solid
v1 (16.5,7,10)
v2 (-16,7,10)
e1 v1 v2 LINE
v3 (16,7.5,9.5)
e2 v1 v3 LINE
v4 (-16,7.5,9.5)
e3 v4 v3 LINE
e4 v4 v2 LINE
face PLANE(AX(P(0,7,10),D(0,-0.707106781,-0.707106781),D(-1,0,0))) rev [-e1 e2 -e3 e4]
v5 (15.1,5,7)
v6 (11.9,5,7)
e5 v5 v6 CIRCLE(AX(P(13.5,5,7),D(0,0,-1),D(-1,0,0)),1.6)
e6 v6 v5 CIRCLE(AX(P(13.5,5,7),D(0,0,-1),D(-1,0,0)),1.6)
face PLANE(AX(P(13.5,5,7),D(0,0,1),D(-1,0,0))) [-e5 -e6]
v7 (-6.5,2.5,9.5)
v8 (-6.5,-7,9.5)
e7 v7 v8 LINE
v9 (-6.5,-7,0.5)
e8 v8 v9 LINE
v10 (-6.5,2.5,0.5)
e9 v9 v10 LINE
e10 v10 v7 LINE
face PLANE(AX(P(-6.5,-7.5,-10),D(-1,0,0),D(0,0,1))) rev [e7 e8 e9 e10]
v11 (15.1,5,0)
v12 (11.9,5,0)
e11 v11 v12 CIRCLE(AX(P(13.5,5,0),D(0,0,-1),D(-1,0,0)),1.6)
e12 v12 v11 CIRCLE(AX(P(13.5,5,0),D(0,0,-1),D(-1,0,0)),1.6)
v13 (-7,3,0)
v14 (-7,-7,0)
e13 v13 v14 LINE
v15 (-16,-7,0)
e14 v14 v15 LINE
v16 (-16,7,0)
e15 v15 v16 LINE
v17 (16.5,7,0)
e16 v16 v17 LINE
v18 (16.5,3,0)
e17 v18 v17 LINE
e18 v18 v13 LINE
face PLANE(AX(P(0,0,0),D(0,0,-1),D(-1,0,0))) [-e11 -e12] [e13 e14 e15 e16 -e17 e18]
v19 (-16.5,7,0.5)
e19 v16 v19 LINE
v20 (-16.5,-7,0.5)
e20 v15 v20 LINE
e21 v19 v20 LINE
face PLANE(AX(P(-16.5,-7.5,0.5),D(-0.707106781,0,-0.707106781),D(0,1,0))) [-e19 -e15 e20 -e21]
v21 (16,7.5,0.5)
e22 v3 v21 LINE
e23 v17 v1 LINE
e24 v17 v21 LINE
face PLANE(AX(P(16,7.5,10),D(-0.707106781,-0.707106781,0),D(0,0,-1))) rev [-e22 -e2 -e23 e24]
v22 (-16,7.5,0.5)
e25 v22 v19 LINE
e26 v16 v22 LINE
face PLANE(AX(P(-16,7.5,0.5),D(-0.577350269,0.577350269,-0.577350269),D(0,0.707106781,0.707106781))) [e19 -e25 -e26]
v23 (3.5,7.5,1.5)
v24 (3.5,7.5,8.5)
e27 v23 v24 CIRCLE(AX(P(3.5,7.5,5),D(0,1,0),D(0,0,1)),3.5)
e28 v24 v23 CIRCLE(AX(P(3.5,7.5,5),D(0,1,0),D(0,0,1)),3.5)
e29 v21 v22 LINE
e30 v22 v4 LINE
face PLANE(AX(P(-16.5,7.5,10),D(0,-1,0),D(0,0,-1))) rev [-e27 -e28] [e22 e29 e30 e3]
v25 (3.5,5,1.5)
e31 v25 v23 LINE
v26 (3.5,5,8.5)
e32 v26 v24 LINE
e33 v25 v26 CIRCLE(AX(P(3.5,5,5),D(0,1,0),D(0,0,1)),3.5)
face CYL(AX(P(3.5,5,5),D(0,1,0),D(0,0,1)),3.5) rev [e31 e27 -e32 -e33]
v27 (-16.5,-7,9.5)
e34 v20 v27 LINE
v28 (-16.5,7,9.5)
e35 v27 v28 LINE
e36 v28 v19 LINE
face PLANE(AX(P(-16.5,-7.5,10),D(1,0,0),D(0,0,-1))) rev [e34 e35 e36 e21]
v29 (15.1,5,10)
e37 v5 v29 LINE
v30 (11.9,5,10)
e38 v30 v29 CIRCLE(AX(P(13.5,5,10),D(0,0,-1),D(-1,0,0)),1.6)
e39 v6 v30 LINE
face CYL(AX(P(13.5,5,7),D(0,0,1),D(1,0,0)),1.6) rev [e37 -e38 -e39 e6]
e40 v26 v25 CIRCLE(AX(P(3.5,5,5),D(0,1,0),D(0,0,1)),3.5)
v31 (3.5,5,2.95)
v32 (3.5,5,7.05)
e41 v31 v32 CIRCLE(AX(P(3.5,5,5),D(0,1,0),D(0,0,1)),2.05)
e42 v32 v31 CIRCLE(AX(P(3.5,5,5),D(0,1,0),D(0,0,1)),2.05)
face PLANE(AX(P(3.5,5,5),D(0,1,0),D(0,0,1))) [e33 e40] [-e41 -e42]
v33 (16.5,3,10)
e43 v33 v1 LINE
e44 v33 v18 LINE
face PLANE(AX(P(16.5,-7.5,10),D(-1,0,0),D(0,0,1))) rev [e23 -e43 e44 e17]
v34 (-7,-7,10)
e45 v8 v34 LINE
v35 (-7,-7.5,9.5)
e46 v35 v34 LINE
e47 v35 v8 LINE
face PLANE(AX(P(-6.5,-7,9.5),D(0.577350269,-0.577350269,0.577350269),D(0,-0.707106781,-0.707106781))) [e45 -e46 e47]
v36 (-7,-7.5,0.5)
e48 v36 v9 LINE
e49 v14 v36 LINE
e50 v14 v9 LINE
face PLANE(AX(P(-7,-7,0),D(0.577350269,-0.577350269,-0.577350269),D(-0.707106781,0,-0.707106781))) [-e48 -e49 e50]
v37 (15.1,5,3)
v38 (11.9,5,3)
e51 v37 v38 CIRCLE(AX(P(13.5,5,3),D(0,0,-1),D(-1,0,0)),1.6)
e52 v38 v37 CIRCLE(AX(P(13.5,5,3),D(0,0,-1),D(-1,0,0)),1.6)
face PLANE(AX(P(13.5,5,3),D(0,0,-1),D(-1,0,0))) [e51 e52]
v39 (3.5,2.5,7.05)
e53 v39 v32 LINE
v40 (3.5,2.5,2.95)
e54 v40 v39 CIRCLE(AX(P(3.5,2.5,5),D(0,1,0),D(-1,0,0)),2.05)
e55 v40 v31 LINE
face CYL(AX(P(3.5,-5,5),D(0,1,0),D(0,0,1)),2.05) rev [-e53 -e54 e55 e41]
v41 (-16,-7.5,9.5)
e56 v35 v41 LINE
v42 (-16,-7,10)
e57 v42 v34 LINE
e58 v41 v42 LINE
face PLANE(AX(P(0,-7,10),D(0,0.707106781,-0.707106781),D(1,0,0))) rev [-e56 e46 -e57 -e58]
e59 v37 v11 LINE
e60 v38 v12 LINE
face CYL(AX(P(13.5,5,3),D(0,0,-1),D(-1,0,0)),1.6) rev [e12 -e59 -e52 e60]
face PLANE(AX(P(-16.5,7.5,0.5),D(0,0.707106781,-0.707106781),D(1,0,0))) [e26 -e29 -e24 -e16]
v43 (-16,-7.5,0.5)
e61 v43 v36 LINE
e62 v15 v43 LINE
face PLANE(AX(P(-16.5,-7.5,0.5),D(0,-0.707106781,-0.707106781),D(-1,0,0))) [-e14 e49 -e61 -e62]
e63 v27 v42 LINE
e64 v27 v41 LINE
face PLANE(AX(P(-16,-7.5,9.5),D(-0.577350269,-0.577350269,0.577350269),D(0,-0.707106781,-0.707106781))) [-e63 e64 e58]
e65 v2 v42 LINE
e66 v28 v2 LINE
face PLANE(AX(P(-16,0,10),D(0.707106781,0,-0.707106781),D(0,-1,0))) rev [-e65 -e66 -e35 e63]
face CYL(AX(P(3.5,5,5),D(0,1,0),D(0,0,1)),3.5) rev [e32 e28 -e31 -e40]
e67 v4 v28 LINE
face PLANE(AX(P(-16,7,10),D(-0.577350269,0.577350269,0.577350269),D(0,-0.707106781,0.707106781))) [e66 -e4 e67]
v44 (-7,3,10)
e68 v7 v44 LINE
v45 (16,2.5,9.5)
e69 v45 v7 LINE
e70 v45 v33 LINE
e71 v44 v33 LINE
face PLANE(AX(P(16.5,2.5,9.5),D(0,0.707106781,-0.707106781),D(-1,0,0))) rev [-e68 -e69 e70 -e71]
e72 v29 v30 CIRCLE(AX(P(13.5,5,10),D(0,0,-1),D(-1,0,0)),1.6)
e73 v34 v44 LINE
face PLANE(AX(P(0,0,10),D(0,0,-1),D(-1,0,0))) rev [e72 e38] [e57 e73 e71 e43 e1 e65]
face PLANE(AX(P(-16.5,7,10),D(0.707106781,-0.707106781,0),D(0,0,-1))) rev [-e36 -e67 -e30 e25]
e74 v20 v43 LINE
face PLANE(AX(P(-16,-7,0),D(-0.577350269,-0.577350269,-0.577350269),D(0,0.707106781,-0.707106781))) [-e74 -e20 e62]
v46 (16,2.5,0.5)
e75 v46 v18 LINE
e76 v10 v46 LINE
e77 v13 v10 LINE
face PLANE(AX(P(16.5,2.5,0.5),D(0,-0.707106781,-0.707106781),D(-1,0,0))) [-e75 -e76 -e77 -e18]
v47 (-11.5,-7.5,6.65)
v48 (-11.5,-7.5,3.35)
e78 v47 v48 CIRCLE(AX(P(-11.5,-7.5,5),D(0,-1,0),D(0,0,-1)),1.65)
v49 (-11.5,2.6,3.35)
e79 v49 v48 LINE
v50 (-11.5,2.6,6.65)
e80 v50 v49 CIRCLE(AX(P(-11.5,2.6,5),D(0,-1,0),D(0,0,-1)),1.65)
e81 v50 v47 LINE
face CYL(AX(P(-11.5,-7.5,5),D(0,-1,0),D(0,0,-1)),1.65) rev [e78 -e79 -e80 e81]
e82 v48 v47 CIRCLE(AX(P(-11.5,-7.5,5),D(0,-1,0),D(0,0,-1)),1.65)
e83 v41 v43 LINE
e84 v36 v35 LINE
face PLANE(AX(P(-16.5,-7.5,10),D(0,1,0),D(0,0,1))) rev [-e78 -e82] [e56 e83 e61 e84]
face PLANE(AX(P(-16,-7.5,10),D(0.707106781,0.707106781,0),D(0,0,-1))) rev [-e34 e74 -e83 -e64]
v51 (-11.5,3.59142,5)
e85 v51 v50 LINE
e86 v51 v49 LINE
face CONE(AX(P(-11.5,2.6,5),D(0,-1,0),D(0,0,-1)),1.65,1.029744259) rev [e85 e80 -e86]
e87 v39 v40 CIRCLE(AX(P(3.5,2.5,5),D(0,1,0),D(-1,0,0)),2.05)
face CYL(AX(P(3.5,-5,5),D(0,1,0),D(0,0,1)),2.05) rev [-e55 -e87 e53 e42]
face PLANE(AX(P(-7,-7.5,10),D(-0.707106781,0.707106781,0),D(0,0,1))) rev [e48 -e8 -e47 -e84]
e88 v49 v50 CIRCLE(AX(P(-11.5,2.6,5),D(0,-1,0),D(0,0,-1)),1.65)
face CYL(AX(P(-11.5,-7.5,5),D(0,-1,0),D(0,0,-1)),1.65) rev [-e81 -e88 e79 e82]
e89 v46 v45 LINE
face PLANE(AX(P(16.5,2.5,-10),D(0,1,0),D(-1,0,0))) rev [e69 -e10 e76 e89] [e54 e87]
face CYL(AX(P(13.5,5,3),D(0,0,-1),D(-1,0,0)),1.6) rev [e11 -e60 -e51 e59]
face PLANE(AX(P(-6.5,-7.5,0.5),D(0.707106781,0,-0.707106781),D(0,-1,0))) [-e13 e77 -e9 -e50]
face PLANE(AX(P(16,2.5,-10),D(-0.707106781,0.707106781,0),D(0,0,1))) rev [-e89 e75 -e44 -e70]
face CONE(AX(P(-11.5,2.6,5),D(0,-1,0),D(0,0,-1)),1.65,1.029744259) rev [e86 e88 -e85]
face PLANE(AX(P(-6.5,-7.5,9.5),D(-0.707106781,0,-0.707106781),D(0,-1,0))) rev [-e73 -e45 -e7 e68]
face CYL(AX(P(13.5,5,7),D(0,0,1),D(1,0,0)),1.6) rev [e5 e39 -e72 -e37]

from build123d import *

# Parameters (mm, degrees)
SKETCH1_W             = 33
SKETCH1_H             = 15
BOSS_EXTRUDE1_DEPTH   = 10
SKETCH2_W             = 23
SKETCH2_H             = 10
CUT_EXTRUDE1_DEPTH    = 20
M4_TAPPED_HOLE1_D     = 3.3
M4_TAPPED_HOLE1_DEPTH = 10.1
M4_TAPPED_HOLE1_TIP   = 0.991420021
CHAMFER1_SIZE         = 0.5
SKETCH6_R             = 3.5
CUT_EXTRUDE3_DEPTH    = 2.5
SKETCH7_R             = 1.6
CUT_EXTRUDE4_DEPTH    = 3
SKETCH8_R             = 2.05
CUT_EXTRUDE5_DEPTH    = 10


with BuildPart() as part:
    # Sketch1 → Boss-Extrude1 (new body)
    with BuildSketch(Plane.XY):
        Rectangle(SKETCH1_W, SKETCH1_H)
    extrude(amount=BOSS_EXTRUDE1_DEPTH)

    # Sketch2 → Cut-Extrude1 (cut)
    with BuildSketch(Plane.XY.offset(10)):
        with Locations((5, -2.5)):
            Rectangle(SKETCH2_W, SKETCH2_H)
    extrude(amount=-CUT_EXTRUDE1_DEPTH, mode=Mode.SUBTRACT)

    # M4 Tapped Hole1
    with Locations(Plane(origin=(0, -7.5, 0), x_dir=(-1, 0, 0), z_dir=(0, -1, 0))):
        with Locations((11.5, -5)):
            Hole(M4_TAPPED_HOLE1_D / 2, depth=M4_TAPPED_HOLE1_DEPTH)
            with Locations((0, 0, -(M4_TAPPED_HOLE1_DEPTH + M4_TAPPED_HOLE1_TIP / 2))):  # 118° drill point
                Cone(0, M4_TAPPED_HOLE1_D / 2, M4_TAPPED_HOLE1_TIP, mode=Mode.SUBTRACT)

    # Chamfer1
    chamfer1_edges = [part.edges().sort_by_distance(p)[0] for p in [
        (-16.5, 0, 10),
        (-11.5, -7.5, 10),
        (5, 2.5, 0),
        (-6.5, -2.5, 0),
        (16.5, 2.5, 5),
        (-6.5, -7.5, 5),
        (5, 2.5, 10),
        (-6.5, -2.5, 10),
        (-11.5, -7.5, 0),
        (-16.5, 0, 0),
        (0, 7.5, 0),
        (0, 7.5, 10),
        (-16.5, -7.5, 5),
        (-16.5, 7.5, 5),
        (16.5, 7.5, 5),
    ]]
    chamfer(chamfer1_edges, length=CHAMFER1_SIZE)

    # Sketch6 → Cut-Extrude3 (cut)
    with BuildSketch(Plane(origin=(0, 7.5, 0), x_dir=(1, 0, 0), z_dir=(0, 1, 0))):
        with Locations(Location((3.5, -5, 0), (0, 0, 270))):
            Circle(SKETCH6_R)
    extrude(amount=-CUT_EXTRUDE3_DEPTH, mode=Mode.SUBTRACT)

    # Sketch7 → Cut-Extrude4 (cut)
    with BuildSketch(Plane(origin=(0, 0, 0), x_dir=(-1, 0, 0), z_dir=(0, 0, -1))):
        with Locations((-13.5, 5)):
            Circle(SKETCH7_R)
    cut_extrude4 = extrude(amount=-CUT_EXTRUDE4_DEPTH, mode=Mode.SUBTRACT)

    # Mirror1: Cut-Extrude4 across plane
    add(cut_extrude4.mirror(Plane(origin=(0, 0, 5), x_dir=(1, 0, 0), z_dir=(0, 0, -1))), mode=Mode.SUBTRACT)

    # Sketch8 → Cut-Extrude5 (cut)
    with BuildSketch(Plane(origin=(0, 5, 0), x_dir=(1, 0, 0), z_dir=(0, 1, 0))):
        with Locations(Location((3.5, -5, 0), (0, 0, 270))):
            Circle(SKETCH8_R)
    extrude(amount=-CUT_EXTRUDE5_DEPTH, mode=Mode.SUBTRACT)


solid = part.part
